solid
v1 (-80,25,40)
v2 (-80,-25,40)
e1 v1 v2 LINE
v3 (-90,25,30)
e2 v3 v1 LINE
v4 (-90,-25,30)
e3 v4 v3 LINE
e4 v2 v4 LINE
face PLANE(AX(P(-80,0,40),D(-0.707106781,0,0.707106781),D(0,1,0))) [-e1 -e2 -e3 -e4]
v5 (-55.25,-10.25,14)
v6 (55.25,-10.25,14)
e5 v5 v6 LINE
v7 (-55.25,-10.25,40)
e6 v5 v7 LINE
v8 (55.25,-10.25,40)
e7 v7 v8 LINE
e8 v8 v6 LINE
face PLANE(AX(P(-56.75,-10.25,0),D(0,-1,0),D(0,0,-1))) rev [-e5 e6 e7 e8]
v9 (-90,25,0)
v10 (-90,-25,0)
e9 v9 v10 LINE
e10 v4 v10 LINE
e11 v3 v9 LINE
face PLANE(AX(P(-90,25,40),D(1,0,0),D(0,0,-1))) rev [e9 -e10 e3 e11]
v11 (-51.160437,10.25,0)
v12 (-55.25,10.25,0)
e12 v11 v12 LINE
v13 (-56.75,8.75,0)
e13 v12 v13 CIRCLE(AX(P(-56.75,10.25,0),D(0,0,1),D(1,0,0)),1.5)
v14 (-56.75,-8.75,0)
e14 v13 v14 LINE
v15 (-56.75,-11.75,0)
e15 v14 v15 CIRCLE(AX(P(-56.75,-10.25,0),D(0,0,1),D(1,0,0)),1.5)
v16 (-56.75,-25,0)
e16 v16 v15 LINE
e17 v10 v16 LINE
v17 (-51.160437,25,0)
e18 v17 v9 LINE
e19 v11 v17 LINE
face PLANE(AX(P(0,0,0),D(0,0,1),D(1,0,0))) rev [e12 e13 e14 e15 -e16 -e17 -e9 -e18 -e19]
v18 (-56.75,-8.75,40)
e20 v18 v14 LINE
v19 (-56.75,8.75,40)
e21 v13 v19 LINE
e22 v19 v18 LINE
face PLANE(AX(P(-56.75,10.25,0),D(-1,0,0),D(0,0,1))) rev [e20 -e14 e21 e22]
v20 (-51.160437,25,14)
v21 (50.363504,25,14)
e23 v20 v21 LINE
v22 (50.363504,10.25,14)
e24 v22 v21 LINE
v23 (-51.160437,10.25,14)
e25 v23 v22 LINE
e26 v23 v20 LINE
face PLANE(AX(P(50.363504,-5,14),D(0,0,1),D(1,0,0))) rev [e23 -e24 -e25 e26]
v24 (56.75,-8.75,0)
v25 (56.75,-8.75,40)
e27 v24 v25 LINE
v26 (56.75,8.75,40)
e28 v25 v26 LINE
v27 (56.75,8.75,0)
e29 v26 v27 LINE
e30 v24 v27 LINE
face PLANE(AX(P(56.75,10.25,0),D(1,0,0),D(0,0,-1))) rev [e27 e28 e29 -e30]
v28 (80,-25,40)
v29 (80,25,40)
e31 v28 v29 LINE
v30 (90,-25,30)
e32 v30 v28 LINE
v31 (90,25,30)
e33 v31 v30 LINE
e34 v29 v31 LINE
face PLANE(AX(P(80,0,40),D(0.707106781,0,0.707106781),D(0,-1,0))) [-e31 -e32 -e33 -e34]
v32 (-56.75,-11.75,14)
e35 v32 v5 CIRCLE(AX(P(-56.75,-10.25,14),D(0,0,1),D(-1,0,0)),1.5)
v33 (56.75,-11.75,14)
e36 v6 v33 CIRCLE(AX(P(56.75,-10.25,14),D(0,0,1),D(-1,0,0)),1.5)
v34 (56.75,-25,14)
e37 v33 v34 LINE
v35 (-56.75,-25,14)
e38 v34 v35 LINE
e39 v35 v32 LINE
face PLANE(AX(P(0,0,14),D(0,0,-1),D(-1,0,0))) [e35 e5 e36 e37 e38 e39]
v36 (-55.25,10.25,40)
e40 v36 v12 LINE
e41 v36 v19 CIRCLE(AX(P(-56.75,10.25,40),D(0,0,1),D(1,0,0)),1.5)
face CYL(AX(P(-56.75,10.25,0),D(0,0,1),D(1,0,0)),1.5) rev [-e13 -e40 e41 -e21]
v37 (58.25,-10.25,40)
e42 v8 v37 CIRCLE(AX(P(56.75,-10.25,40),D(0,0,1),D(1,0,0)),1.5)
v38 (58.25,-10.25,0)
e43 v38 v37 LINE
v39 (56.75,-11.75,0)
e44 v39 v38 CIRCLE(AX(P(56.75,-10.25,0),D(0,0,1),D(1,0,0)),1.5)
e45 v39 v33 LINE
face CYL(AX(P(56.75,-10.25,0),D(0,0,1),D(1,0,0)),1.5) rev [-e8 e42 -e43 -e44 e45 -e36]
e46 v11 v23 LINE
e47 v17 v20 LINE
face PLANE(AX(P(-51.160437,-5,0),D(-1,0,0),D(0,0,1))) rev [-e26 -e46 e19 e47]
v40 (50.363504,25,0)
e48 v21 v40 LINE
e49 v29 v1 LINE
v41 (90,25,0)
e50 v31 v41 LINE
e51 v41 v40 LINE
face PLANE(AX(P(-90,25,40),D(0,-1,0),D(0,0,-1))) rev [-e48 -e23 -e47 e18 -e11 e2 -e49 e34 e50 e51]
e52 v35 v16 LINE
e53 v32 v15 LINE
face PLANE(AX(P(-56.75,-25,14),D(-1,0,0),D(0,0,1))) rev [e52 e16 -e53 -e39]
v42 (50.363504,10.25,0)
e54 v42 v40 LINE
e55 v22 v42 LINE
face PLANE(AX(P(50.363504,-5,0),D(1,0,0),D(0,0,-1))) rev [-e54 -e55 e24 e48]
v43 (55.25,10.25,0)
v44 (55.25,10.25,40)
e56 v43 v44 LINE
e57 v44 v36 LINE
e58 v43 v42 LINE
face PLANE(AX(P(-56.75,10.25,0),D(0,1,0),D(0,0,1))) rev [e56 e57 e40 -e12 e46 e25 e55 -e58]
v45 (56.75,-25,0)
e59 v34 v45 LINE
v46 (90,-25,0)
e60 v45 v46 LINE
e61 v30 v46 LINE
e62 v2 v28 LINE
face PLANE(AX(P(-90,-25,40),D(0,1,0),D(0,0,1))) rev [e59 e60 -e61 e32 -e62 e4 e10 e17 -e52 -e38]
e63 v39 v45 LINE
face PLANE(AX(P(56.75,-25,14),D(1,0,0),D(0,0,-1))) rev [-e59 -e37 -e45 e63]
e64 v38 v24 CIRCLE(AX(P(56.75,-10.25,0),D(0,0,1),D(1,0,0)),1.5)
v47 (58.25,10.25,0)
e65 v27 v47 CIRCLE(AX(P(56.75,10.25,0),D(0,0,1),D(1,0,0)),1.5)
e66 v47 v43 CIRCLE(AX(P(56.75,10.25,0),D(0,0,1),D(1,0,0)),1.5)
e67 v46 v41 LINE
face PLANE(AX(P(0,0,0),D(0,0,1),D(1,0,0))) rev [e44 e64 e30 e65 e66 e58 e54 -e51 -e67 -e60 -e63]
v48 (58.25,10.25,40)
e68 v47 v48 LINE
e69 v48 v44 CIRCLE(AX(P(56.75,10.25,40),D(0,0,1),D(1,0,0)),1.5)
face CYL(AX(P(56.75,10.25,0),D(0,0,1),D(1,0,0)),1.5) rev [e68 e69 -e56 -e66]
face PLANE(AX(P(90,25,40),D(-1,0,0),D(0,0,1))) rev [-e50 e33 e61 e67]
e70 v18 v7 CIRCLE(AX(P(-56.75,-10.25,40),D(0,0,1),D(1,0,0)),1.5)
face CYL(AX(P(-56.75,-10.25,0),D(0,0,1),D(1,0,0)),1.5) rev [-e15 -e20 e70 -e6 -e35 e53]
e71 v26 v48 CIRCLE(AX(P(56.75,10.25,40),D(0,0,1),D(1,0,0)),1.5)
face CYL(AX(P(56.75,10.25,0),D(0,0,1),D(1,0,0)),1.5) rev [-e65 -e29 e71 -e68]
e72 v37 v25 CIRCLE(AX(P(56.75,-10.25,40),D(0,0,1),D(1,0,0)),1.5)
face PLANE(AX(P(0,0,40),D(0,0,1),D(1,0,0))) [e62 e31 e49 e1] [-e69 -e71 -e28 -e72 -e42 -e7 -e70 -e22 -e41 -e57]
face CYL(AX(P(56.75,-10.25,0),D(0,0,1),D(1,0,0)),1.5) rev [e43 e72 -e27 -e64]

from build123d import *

# Parameters (mm, degrees)
SKETCH1_W           = 180
SKETCH1_H           = 50
BOSS_EXTRUDE1_DEPTH = 40
SKETCH2_W           = 113.5
SKETCH2_H           = 20.5
CUT_EXTRUDE1_DEPTH  = 102.612007165
SKETCH3_R           = 1.5
CUT_EXTRUDE2_DEPTH  = 102.612007165
SKETCH4_W           = 101.523941395
SKETCH4_H           = 14
CUT_EXTRUDE3_DEPTH  = 30
SKETCH5_W           = 113.5
SKETCH5_H           = 14.75
CUT_EXTRUDE4_DEPTH  = 14
CHAMFER1_SIZE       = 10


with BuildPart() as part:
    # Sketch1 → Boss-Extrude1 (new body)
    with BuildSketch(Plane.XY):
        Rectangle(SKETCH1_W, SKETCH1_H)
    extrude(amount=BOSS_EXTRUDE1_DEPTH)

    # Sketch2 → Cut-Extrude1 (cut, through all)
    with BuildSketch(Plane.XY.offset(40)):
        Rectangle(SKETCH2_W, SKETCH2_H)
    extrude(amount=-CUT_EXTRUDE1_DEPTH, mode=Mode.SUBTRACT)

    # Sketch3 → Cut-Extrude2 (cut, through all)
    with BuildSketch(Plane.XY.offset(40)):
        with Locations((-56.75, 10.25)):
            Circle(SKETCH3_R)
        with Locations((-56.75, -10.25)):
            Circle(SKETCH3_R)
        with Locations((56.75, 10.25)):
            Circle(SKETCH3_R)
        with Locations((56.75, -10.25)):
            Circle(SKETCH3_R)
    extrude(amount=-CUT_EXTRUDE2_DEPTH, mode=Mode.SUBTRACT)

    # Sketch4 → Cut-Extrude3 (cut)
    with BuildSketch(Plane(origin=(0, 25, 0), x_dir=(1, 0, 0), z_dir=(0, 1, 0))):
        with Locations((-0.398466407, -7)):
            Rectangle(SKETCH4_W, SKETCH4_H)
    extrude(amount=-CUT_EXTRUDE3_DEPTH, mode=Mode.SUBTRACT)

    # Sketch5 → Cut-Extrude4 (cut)
    with BuildSketch(Plane(origin=(0, 0, 0), x_dir=(-1, 0, 0), z_dir=(0, 0, -1))):
        with Locations((0, -17.625)):
            Rectangle(SKETCH5_W, SKETCH5_H)
    extrude(amount=-CUT_EXTRUDE4_DEPTH, mode=Mode.SUBTRACT)

    # Chamfer1
    chamfer1_edges = [part.edges().sort_by_distance(p)[0] for p in [
        (90, 0, 40),
        (-90, 0, 40),
    ]]
    chamfer(chamfer1_edges, length=CHAMFER1_SIZE)


solid = part.part
